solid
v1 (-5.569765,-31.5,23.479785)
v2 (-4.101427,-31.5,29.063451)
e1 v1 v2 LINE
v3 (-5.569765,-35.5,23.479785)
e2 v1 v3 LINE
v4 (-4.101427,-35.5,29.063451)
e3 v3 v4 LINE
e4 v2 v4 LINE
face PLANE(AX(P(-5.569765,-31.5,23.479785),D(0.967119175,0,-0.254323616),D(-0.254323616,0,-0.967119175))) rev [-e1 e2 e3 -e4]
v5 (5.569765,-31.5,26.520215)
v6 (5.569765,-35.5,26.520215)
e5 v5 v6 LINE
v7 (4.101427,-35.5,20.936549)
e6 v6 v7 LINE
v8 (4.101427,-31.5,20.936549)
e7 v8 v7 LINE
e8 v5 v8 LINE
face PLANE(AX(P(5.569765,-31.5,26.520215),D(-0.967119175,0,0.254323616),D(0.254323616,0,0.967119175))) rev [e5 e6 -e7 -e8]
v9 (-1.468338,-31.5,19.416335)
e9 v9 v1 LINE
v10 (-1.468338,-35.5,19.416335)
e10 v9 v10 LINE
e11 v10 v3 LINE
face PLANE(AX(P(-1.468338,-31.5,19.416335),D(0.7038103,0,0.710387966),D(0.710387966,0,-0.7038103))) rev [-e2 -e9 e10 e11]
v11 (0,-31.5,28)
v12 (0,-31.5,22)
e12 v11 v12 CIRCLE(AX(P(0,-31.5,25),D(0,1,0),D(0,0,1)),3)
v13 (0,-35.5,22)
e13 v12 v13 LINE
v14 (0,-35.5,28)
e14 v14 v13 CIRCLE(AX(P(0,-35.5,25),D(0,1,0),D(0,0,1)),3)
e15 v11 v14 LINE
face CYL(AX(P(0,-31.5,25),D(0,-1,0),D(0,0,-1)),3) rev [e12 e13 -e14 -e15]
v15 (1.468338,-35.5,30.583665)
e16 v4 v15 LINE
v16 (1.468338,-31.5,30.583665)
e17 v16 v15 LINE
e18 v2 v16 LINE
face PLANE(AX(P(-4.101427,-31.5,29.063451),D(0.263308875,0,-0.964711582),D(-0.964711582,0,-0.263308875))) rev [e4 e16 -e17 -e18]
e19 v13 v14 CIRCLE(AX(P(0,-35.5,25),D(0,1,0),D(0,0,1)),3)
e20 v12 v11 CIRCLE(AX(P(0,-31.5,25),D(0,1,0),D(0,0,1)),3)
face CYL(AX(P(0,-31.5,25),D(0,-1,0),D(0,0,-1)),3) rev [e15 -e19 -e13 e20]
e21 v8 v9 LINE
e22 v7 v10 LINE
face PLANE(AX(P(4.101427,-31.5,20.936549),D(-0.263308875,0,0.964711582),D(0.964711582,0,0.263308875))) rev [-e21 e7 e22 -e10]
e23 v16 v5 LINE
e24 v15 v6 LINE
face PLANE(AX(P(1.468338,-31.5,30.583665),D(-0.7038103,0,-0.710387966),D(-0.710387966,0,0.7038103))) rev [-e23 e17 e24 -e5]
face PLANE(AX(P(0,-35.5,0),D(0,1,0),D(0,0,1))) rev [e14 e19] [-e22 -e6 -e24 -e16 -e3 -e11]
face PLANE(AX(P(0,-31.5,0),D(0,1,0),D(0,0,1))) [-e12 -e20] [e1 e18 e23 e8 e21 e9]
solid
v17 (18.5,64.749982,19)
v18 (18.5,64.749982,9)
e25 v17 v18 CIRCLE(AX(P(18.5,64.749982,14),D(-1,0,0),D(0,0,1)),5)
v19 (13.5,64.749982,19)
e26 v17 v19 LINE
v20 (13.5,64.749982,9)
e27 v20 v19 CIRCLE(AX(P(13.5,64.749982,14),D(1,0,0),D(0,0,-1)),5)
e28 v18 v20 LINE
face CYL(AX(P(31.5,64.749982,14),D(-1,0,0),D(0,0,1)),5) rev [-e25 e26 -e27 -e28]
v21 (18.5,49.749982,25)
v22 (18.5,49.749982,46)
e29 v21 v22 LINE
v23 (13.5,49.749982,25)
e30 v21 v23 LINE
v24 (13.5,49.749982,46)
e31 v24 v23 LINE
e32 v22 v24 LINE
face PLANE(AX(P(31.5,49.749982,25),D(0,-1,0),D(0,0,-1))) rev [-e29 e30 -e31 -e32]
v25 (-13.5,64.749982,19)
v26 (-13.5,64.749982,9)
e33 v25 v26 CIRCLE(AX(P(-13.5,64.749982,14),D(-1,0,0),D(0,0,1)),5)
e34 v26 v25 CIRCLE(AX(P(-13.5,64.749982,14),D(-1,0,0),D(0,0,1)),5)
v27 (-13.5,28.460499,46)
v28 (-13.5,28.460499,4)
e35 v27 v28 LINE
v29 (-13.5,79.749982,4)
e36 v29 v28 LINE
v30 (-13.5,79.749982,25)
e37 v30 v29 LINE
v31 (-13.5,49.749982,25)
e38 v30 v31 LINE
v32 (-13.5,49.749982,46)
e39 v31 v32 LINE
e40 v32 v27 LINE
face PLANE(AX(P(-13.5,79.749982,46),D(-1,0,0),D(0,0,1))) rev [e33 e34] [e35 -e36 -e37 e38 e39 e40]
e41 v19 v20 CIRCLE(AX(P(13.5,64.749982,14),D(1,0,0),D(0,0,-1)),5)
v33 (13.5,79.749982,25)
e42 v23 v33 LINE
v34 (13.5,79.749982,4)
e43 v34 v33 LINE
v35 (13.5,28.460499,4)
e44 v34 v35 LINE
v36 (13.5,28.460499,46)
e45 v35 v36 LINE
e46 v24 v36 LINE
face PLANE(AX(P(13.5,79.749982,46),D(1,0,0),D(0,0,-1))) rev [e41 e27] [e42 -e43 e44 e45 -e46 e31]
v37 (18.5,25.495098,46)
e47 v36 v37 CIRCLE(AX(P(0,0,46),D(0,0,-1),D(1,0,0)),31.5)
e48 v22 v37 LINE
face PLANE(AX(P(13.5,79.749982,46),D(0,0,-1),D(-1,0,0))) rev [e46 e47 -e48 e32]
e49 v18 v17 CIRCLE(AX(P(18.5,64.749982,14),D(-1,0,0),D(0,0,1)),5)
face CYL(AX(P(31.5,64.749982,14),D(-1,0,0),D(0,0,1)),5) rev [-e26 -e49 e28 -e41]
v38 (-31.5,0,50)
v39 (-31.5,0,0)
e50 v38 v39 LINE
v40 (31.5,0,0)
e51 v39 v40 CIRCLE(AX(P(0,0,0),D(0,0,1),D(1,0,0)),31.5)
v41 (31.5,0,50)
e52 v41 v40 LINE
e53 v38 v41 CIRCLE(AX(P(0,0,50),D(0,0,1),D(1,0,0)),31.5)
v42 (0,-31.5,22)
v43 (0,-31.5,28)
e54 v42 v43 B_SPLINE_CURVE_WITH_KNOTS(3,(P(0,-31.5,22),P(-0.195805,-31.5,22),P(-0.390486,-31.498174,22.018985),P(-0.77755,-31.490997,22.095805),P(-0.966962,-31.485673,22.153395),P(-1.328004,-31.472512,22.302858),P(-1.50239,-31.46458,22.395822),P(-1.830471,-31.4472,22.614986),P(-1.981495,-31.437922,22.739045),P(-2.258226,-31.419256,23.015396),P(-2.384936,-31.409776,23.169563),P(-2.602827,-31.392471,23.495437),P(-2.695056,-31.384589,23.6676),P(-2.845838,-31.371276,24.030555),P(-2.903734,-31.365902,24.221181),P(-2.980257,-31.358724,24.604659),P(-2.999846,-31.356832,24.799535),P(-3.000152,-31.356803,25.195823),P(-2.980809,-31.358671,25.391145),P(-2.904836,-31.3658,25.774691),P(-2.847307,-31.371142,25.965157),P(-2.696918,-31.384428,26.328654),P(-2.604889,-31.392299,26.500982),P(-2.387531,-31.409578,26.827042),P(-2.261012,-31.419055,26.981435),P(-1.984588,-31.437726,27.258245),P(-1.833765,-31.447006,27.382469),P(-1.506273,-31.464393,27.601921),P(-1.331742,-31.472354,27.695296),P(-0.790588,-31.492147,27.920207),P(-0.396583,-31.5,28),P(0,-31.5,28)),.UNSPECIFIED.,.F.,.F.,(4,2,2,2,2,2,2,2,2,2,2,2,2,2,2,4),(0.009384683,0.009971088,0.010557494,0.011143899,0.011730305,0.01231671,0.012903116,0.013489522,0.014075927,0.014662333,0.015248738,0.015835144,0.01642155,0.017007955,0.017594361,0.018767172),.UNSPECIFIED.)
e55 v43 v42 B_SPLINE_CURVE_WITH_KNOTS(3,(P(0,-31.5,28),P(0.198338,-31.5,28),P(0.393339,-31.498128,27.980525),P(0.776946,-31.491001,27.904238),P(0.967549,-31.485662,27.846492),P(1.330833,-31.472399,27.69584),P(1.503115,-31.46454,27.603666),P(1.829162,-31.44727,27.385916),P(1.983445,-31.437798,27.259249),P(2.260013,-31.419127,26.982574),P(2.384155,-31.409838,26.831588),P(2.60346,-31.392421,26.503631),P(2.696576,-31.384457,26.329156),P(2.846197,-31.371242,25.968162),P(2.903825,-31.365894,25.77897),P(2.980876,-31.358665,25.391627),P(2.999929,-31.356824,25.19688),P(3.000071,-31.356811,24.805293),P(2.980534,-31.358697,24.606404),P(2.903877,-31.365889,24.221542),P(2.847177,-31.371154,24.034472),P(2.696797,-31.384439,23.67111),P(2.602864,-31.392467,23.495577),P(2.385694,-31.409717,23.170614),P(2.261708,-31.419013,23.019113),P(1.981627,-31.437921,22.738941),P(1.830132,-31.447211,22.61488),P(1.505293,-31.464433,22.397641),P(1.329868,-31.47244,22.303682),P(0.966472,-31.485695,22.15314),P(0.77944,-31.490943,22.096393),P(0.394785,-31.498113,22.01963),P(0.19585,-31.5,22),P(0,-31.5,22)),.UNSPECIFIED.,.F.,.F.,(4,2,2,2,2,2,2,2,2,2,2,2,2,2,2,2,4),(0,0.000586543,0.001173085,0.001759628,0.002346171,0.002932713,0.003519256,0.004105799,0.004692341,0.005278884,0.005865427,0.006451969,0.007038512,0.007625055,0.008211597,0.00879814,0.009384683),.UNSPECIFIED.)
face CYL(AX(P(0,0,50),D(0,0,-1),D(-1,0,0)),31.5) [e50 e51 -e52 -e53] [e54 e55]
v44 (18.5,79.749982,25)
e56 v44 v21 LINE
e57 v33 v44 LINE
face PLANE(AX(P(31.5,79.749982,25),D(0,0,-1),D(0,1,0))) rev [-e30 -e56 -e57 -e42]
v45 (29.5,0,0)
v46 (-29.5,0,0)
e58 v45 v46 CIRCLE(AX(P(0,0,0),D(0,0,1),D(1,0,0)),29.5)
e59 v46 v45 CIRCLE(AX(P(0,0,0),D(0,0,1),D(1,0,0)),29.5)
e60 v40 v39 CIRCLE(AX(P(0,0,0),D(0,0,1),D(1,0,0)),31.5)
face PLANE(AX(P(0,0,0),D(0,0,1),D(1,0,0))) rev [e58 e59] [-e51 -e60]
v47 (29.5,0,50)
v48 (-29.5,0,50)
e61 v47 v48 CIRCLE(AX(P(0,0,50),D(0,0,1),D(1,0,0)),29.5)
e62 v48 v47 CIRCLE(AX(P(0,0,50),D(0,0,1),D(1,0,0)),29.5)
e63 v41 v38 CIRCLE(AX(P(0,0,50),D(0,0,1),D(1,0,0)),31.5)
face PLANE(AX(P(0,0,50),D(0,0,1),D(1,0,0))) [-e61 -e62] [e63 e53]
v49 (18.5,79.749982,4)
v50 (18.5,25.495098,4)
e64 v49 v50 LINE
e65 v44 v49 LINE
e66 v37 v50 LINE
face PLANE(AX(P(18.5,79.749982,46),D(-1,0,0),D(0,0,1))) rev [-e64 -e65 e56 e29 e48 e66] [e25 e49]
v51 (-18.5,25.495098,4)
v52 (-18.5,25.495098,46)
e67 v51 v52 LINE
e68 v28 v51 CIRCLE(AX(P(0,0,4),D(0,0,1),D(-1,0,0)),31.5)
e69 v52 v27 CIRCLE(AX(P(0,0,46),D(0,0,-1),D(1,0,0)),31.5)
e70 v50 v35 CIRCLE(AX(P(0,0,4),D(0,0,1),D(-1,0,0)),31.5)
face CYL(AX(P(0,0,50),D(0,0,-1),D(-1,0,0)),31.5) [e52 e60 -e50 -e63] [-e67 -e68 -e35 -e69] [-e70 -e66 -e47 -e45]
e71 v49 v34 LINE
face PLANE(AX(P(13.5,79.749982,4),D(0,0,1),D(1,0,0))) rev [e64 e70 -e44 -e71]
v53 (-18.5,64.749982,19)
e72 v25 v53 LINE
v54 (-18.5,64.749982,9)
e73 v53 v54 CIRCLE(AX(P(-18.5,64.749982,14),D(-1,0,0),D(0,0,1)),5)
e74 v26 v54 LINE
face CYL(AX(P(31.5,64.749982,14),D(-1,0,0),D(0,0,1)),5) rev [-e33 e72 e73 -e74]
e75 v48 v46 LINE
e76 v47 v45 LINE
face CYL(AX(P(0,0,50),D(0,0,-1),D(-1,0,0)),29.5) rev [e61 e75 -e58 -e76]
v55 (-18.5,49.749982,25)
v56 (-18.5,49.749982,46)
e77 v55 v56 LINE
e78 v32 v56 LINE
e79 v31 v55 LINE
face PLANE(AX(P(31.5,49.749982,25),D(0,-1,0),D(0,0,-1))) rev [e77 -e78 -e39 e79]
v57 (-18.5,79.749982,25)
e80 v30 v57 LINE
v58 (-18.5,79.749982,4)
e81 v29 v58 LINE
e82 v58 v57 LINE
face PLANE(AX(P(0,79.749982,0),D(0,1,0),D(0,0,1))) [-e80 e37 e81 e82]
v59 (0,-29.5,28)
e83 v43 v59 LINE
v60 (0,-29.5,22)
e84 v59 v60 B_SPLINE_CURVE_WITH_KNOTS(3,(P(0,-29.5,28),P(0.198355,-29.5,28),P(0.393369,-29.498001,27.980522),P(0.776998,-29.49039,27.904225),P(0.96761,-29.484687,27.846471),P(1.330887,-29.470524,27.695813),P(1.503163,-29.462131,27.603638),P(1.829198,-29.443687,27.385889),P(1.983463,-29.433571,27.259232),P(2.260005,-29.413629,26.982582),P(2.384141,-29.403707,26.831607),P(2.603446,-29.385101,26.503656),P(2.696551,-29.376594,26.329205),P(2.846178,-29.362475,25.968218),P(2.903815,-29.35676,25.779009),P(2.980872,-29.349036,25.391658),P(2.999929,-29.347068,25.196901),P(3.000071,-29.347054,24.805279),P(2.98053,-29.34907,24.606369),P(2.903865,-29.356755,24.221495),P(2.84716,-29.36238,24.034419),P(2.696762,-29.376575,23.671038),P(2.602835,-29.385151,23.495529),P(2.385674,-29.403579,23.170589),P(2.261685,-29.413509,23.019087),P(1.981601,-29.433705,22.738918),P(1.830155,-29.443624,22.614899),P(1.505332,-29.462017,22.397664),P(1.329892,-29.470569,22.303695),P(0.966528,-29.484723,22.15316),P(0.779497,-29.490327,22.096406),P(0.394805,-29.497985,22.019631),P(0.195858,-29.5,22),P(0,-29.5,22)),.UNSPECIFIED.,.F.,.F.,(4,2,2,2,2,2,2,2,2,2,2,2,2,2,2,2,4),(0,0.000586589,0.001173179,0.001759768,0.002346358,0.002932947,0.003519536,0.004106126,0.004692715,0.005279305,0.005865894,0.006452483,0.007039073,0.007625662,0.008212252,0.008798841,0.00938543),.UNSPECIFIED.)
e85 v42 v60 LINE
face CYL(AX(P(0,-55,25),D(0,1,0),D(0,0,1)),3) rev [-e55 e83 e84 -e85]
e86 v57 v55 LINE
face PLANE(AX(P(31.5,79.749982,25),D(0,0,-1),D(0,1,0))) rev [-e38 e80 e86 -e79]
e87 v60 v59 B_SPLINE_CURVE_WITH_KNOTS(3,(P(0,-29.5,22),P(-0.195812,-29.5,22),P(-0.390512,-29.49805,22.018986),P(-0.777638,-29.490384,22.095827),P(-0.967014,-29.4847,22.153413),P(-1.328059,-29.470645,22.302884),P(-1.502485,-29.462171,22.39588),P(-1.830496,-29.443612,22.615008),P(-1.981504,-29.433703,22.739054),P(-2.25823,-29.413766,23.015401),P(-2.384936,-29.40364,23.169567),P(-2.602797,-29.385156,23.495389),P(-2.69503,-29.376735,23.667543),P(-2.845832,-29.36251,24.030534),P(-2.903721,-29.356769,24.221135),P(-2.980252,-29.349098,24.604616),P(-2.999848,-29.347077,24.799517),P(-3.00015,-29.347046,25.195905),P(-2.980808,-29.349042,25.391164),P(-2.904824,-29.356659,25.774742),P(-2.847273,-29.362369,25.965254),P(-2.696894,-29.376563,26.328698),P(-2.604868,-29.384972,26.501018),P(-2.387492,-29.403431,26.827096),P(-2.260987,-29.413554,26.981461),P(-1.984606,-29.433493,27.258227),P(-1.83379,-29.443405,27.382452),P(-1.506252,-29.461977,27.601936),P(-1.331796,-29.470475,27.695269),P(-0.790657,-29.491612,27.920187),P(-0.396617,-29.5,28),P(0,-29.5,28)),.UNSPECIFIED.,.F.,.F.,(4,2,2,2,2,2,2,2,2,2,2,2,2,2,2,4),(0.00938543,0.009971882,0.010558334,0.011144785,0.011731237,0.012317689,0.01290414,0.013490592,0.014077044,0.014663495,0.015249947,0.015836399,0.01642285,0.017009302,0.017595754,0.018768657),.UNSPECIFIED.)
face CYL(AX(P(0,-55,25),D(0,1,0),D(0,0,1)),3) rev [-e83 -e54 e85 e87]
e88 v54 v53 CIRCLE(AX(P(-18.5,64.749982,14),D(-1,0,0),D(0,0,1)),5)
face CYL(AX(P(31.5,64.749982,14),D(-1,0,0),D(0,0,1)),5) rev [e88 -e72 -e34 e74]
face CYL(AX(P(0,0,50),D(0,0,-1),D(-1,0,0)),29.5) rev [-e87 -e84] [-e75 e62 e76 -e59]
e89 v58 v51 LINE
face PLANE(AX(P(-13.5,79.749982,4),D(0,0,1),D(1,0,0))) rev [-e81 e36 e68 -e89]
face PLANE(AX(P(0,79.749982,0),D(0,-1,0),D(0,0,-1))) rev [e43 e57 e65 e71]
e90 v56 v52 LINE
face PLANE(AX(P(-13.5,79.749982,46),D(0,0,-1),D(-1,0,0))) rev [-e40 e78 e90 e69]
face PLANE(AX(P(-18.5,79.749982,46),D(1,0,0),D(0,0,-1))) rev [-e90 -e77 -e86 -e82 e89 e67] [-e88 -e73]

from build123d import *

# Parameters (mm, degrees)
SKETCH1_R                       = 31.5
SKETCH1_R_2                     = 29.5
BOSS_EXTRUDE1_DEPTH             = 50
BOSS_EXTRUDE2_REACH             = 102.468
BOSS_EXTRUDE2_END_RADIUS        = 31.5
SKETCH2_W                       = 5
SKETCH2_H                       = 42
BOSS_EXTRUDE2_DIRECTION_2_DEPTH = 30
SKETCH4_W                       = 21
SKETCH4_H                       = 30
CUT_EXTRUDE1_DEPTH              = 50
SKETCH5_R                       = 5
CUT_EXTRUDE2_DEPTH              = 50
SKETCH6_R                       = 3
CUT_EXTRUDE3_DEPTH              = 55
SKETCH7_R                       = 3
BOSS_EXTRUDE3_DEPTH             = 4


with BuildPart() as part:
    # Sketch1 → Boss-Extrude1 (new body)
    with BuildSketch(Plane.XY):
        Circle(SKETCH1_R)
        Circle(SKETCH1_R_2, mode=Mode.SUBTRACT)
    extrude(amount=BOSS_EXTRUDE1_DEPTH)

    # Boss-Extrude2: up to this cylinder (the profile starts outside it)
    boss_extrude2_end = Plane(origin=(0, 0, 25), z_dir=(0, 0, -1)) * Cylinder(BOSS_EXTRUDE2_END_RADIUS, 268.936, mode=Mode.PRIVATE)
    # Sketch2 → Boss-Extrude2 (add, up to the surface)
    with BuildSketch(Plane(origin=(0, 49.74998211, 0), x_dir=(1, 0, 0), z_dir=(0, 1, 0)), mode=Mode.PRIVATE) as boss_extrude2_sk1:
        with Locations((-16, -25)):
            Rectangle(SKETCH2_W, SKETCH2_H)
    boss_extrude2_tool1 = extrude(boss_extrude2_sk1.sketch, amount=-BOSS_EXTRUDE2_REACH, mode=Mode.PRIVATE) - boss_extrude2_end
    add(boss_extrude2_tool1.solids().sort_by_distance((-16, 49.749982, 25))[0])
    # Sketch2 → Boss-Extrude2 (add, up to the surface)
    with BuildSketch(Plane(origin=(0, 49.74998211, 0), x_dir=(1, 0, 0), z_dir=(0, 1, 0)), mode=Mode.PRIVATE) as boss_extrude2_sk2:
        with Locations((16, -25)):
            Rectangle(SKETCH2_W, SKETCH2_H)
    boss_extrude2_tool2 = extrude(boss_extrude2_sk2.sketch, amount=-BOSS_EXTRUDE2_REACH, mode=Mode.PRIVATE) - boss_extrude2_end
    add(boss_extrude2_tool2.solids().sort_by_distance((16, 49.749982, 25))[0])

    # Sketch2 → Boss-Extrude2 direction 2 (add)
    with BuildSketch(Plane(origin=(0, 49.74998211, 0), x_dir=(1, 0, 0), z_dir=(0, 1, 0))):
        with Locations((-16, -25)):
            Rectangle(SKETCH2_W, SKETCH2_H)
        with Locations((16, -25)):
            Rectangle(SKETCH2_W, SKETCH2_H)
    extrude(amount=BOSS_EXTRUDE2_DIRECTION_2_DEPTH)

    # Sketch4 → Cut-Extrude1 (cut)
    with BuildSketch(Plane.ZY.offset(18.5)):
        with Locations((35.5, 64.74998211)):
            Rectangle(SKETCH4_W, SKETCH4_H)
    extrude(amount=-CUT_EXTRUDE1_DEPTH, mode=Mode.SUBTRACT)

    # Sketch5 → Cut-Extrude2 (cut)
    with BuildSketch(Plane.ZY.offset(18.5)):
        with Locations((14, 64.74998211)):
            Circle(SKETCH5_R)
    extrude(amount=-CUT_EXTRUDE2_DEPTH, mode=Mode.SUBTRACT)

    # Sketch6 → Cut-Extrude3 (cut)
    with BuildSketch(Plane(origin=(0, 0, 0), x_dir=(1, 0, 0), z_dir=(0, 1, 0))):
        with Locations(Location((0, -25, 0), (0, 0, 270))):
            Circle(SKETCH6_R)
    extrude(amount=-CUT_EXTRUDE3_DEPTH, mode=Mode.SUBTRACT)


with BuildPart() as body_2:
    # Sketch7 → Boss-Extrude3 (new body)
    with BuildSketch(Plane(origin=(0, -35.5, 0), x_dir=(1, 0, 0), z_dir=(0, 1, 0))):
        Polygon((-4.101426834, -29.063450659), (1.468338081, -30.583665159), (5.569764915, -26.5202145), (4.101426834, -20.936549341), (-1.468338081, -19.416334841), (-5.569764915, -23.4797855), align=None)
        with Locations(Location((0, -25, 0), (0, 0, 270))):
            Circle(SKETCH7_R, mode=Mode.SUBTRACT)
    extrude(amount=BOSS_EXTRUDE3_DEPTH)


solid = Compound([part.part, body_2.part])
